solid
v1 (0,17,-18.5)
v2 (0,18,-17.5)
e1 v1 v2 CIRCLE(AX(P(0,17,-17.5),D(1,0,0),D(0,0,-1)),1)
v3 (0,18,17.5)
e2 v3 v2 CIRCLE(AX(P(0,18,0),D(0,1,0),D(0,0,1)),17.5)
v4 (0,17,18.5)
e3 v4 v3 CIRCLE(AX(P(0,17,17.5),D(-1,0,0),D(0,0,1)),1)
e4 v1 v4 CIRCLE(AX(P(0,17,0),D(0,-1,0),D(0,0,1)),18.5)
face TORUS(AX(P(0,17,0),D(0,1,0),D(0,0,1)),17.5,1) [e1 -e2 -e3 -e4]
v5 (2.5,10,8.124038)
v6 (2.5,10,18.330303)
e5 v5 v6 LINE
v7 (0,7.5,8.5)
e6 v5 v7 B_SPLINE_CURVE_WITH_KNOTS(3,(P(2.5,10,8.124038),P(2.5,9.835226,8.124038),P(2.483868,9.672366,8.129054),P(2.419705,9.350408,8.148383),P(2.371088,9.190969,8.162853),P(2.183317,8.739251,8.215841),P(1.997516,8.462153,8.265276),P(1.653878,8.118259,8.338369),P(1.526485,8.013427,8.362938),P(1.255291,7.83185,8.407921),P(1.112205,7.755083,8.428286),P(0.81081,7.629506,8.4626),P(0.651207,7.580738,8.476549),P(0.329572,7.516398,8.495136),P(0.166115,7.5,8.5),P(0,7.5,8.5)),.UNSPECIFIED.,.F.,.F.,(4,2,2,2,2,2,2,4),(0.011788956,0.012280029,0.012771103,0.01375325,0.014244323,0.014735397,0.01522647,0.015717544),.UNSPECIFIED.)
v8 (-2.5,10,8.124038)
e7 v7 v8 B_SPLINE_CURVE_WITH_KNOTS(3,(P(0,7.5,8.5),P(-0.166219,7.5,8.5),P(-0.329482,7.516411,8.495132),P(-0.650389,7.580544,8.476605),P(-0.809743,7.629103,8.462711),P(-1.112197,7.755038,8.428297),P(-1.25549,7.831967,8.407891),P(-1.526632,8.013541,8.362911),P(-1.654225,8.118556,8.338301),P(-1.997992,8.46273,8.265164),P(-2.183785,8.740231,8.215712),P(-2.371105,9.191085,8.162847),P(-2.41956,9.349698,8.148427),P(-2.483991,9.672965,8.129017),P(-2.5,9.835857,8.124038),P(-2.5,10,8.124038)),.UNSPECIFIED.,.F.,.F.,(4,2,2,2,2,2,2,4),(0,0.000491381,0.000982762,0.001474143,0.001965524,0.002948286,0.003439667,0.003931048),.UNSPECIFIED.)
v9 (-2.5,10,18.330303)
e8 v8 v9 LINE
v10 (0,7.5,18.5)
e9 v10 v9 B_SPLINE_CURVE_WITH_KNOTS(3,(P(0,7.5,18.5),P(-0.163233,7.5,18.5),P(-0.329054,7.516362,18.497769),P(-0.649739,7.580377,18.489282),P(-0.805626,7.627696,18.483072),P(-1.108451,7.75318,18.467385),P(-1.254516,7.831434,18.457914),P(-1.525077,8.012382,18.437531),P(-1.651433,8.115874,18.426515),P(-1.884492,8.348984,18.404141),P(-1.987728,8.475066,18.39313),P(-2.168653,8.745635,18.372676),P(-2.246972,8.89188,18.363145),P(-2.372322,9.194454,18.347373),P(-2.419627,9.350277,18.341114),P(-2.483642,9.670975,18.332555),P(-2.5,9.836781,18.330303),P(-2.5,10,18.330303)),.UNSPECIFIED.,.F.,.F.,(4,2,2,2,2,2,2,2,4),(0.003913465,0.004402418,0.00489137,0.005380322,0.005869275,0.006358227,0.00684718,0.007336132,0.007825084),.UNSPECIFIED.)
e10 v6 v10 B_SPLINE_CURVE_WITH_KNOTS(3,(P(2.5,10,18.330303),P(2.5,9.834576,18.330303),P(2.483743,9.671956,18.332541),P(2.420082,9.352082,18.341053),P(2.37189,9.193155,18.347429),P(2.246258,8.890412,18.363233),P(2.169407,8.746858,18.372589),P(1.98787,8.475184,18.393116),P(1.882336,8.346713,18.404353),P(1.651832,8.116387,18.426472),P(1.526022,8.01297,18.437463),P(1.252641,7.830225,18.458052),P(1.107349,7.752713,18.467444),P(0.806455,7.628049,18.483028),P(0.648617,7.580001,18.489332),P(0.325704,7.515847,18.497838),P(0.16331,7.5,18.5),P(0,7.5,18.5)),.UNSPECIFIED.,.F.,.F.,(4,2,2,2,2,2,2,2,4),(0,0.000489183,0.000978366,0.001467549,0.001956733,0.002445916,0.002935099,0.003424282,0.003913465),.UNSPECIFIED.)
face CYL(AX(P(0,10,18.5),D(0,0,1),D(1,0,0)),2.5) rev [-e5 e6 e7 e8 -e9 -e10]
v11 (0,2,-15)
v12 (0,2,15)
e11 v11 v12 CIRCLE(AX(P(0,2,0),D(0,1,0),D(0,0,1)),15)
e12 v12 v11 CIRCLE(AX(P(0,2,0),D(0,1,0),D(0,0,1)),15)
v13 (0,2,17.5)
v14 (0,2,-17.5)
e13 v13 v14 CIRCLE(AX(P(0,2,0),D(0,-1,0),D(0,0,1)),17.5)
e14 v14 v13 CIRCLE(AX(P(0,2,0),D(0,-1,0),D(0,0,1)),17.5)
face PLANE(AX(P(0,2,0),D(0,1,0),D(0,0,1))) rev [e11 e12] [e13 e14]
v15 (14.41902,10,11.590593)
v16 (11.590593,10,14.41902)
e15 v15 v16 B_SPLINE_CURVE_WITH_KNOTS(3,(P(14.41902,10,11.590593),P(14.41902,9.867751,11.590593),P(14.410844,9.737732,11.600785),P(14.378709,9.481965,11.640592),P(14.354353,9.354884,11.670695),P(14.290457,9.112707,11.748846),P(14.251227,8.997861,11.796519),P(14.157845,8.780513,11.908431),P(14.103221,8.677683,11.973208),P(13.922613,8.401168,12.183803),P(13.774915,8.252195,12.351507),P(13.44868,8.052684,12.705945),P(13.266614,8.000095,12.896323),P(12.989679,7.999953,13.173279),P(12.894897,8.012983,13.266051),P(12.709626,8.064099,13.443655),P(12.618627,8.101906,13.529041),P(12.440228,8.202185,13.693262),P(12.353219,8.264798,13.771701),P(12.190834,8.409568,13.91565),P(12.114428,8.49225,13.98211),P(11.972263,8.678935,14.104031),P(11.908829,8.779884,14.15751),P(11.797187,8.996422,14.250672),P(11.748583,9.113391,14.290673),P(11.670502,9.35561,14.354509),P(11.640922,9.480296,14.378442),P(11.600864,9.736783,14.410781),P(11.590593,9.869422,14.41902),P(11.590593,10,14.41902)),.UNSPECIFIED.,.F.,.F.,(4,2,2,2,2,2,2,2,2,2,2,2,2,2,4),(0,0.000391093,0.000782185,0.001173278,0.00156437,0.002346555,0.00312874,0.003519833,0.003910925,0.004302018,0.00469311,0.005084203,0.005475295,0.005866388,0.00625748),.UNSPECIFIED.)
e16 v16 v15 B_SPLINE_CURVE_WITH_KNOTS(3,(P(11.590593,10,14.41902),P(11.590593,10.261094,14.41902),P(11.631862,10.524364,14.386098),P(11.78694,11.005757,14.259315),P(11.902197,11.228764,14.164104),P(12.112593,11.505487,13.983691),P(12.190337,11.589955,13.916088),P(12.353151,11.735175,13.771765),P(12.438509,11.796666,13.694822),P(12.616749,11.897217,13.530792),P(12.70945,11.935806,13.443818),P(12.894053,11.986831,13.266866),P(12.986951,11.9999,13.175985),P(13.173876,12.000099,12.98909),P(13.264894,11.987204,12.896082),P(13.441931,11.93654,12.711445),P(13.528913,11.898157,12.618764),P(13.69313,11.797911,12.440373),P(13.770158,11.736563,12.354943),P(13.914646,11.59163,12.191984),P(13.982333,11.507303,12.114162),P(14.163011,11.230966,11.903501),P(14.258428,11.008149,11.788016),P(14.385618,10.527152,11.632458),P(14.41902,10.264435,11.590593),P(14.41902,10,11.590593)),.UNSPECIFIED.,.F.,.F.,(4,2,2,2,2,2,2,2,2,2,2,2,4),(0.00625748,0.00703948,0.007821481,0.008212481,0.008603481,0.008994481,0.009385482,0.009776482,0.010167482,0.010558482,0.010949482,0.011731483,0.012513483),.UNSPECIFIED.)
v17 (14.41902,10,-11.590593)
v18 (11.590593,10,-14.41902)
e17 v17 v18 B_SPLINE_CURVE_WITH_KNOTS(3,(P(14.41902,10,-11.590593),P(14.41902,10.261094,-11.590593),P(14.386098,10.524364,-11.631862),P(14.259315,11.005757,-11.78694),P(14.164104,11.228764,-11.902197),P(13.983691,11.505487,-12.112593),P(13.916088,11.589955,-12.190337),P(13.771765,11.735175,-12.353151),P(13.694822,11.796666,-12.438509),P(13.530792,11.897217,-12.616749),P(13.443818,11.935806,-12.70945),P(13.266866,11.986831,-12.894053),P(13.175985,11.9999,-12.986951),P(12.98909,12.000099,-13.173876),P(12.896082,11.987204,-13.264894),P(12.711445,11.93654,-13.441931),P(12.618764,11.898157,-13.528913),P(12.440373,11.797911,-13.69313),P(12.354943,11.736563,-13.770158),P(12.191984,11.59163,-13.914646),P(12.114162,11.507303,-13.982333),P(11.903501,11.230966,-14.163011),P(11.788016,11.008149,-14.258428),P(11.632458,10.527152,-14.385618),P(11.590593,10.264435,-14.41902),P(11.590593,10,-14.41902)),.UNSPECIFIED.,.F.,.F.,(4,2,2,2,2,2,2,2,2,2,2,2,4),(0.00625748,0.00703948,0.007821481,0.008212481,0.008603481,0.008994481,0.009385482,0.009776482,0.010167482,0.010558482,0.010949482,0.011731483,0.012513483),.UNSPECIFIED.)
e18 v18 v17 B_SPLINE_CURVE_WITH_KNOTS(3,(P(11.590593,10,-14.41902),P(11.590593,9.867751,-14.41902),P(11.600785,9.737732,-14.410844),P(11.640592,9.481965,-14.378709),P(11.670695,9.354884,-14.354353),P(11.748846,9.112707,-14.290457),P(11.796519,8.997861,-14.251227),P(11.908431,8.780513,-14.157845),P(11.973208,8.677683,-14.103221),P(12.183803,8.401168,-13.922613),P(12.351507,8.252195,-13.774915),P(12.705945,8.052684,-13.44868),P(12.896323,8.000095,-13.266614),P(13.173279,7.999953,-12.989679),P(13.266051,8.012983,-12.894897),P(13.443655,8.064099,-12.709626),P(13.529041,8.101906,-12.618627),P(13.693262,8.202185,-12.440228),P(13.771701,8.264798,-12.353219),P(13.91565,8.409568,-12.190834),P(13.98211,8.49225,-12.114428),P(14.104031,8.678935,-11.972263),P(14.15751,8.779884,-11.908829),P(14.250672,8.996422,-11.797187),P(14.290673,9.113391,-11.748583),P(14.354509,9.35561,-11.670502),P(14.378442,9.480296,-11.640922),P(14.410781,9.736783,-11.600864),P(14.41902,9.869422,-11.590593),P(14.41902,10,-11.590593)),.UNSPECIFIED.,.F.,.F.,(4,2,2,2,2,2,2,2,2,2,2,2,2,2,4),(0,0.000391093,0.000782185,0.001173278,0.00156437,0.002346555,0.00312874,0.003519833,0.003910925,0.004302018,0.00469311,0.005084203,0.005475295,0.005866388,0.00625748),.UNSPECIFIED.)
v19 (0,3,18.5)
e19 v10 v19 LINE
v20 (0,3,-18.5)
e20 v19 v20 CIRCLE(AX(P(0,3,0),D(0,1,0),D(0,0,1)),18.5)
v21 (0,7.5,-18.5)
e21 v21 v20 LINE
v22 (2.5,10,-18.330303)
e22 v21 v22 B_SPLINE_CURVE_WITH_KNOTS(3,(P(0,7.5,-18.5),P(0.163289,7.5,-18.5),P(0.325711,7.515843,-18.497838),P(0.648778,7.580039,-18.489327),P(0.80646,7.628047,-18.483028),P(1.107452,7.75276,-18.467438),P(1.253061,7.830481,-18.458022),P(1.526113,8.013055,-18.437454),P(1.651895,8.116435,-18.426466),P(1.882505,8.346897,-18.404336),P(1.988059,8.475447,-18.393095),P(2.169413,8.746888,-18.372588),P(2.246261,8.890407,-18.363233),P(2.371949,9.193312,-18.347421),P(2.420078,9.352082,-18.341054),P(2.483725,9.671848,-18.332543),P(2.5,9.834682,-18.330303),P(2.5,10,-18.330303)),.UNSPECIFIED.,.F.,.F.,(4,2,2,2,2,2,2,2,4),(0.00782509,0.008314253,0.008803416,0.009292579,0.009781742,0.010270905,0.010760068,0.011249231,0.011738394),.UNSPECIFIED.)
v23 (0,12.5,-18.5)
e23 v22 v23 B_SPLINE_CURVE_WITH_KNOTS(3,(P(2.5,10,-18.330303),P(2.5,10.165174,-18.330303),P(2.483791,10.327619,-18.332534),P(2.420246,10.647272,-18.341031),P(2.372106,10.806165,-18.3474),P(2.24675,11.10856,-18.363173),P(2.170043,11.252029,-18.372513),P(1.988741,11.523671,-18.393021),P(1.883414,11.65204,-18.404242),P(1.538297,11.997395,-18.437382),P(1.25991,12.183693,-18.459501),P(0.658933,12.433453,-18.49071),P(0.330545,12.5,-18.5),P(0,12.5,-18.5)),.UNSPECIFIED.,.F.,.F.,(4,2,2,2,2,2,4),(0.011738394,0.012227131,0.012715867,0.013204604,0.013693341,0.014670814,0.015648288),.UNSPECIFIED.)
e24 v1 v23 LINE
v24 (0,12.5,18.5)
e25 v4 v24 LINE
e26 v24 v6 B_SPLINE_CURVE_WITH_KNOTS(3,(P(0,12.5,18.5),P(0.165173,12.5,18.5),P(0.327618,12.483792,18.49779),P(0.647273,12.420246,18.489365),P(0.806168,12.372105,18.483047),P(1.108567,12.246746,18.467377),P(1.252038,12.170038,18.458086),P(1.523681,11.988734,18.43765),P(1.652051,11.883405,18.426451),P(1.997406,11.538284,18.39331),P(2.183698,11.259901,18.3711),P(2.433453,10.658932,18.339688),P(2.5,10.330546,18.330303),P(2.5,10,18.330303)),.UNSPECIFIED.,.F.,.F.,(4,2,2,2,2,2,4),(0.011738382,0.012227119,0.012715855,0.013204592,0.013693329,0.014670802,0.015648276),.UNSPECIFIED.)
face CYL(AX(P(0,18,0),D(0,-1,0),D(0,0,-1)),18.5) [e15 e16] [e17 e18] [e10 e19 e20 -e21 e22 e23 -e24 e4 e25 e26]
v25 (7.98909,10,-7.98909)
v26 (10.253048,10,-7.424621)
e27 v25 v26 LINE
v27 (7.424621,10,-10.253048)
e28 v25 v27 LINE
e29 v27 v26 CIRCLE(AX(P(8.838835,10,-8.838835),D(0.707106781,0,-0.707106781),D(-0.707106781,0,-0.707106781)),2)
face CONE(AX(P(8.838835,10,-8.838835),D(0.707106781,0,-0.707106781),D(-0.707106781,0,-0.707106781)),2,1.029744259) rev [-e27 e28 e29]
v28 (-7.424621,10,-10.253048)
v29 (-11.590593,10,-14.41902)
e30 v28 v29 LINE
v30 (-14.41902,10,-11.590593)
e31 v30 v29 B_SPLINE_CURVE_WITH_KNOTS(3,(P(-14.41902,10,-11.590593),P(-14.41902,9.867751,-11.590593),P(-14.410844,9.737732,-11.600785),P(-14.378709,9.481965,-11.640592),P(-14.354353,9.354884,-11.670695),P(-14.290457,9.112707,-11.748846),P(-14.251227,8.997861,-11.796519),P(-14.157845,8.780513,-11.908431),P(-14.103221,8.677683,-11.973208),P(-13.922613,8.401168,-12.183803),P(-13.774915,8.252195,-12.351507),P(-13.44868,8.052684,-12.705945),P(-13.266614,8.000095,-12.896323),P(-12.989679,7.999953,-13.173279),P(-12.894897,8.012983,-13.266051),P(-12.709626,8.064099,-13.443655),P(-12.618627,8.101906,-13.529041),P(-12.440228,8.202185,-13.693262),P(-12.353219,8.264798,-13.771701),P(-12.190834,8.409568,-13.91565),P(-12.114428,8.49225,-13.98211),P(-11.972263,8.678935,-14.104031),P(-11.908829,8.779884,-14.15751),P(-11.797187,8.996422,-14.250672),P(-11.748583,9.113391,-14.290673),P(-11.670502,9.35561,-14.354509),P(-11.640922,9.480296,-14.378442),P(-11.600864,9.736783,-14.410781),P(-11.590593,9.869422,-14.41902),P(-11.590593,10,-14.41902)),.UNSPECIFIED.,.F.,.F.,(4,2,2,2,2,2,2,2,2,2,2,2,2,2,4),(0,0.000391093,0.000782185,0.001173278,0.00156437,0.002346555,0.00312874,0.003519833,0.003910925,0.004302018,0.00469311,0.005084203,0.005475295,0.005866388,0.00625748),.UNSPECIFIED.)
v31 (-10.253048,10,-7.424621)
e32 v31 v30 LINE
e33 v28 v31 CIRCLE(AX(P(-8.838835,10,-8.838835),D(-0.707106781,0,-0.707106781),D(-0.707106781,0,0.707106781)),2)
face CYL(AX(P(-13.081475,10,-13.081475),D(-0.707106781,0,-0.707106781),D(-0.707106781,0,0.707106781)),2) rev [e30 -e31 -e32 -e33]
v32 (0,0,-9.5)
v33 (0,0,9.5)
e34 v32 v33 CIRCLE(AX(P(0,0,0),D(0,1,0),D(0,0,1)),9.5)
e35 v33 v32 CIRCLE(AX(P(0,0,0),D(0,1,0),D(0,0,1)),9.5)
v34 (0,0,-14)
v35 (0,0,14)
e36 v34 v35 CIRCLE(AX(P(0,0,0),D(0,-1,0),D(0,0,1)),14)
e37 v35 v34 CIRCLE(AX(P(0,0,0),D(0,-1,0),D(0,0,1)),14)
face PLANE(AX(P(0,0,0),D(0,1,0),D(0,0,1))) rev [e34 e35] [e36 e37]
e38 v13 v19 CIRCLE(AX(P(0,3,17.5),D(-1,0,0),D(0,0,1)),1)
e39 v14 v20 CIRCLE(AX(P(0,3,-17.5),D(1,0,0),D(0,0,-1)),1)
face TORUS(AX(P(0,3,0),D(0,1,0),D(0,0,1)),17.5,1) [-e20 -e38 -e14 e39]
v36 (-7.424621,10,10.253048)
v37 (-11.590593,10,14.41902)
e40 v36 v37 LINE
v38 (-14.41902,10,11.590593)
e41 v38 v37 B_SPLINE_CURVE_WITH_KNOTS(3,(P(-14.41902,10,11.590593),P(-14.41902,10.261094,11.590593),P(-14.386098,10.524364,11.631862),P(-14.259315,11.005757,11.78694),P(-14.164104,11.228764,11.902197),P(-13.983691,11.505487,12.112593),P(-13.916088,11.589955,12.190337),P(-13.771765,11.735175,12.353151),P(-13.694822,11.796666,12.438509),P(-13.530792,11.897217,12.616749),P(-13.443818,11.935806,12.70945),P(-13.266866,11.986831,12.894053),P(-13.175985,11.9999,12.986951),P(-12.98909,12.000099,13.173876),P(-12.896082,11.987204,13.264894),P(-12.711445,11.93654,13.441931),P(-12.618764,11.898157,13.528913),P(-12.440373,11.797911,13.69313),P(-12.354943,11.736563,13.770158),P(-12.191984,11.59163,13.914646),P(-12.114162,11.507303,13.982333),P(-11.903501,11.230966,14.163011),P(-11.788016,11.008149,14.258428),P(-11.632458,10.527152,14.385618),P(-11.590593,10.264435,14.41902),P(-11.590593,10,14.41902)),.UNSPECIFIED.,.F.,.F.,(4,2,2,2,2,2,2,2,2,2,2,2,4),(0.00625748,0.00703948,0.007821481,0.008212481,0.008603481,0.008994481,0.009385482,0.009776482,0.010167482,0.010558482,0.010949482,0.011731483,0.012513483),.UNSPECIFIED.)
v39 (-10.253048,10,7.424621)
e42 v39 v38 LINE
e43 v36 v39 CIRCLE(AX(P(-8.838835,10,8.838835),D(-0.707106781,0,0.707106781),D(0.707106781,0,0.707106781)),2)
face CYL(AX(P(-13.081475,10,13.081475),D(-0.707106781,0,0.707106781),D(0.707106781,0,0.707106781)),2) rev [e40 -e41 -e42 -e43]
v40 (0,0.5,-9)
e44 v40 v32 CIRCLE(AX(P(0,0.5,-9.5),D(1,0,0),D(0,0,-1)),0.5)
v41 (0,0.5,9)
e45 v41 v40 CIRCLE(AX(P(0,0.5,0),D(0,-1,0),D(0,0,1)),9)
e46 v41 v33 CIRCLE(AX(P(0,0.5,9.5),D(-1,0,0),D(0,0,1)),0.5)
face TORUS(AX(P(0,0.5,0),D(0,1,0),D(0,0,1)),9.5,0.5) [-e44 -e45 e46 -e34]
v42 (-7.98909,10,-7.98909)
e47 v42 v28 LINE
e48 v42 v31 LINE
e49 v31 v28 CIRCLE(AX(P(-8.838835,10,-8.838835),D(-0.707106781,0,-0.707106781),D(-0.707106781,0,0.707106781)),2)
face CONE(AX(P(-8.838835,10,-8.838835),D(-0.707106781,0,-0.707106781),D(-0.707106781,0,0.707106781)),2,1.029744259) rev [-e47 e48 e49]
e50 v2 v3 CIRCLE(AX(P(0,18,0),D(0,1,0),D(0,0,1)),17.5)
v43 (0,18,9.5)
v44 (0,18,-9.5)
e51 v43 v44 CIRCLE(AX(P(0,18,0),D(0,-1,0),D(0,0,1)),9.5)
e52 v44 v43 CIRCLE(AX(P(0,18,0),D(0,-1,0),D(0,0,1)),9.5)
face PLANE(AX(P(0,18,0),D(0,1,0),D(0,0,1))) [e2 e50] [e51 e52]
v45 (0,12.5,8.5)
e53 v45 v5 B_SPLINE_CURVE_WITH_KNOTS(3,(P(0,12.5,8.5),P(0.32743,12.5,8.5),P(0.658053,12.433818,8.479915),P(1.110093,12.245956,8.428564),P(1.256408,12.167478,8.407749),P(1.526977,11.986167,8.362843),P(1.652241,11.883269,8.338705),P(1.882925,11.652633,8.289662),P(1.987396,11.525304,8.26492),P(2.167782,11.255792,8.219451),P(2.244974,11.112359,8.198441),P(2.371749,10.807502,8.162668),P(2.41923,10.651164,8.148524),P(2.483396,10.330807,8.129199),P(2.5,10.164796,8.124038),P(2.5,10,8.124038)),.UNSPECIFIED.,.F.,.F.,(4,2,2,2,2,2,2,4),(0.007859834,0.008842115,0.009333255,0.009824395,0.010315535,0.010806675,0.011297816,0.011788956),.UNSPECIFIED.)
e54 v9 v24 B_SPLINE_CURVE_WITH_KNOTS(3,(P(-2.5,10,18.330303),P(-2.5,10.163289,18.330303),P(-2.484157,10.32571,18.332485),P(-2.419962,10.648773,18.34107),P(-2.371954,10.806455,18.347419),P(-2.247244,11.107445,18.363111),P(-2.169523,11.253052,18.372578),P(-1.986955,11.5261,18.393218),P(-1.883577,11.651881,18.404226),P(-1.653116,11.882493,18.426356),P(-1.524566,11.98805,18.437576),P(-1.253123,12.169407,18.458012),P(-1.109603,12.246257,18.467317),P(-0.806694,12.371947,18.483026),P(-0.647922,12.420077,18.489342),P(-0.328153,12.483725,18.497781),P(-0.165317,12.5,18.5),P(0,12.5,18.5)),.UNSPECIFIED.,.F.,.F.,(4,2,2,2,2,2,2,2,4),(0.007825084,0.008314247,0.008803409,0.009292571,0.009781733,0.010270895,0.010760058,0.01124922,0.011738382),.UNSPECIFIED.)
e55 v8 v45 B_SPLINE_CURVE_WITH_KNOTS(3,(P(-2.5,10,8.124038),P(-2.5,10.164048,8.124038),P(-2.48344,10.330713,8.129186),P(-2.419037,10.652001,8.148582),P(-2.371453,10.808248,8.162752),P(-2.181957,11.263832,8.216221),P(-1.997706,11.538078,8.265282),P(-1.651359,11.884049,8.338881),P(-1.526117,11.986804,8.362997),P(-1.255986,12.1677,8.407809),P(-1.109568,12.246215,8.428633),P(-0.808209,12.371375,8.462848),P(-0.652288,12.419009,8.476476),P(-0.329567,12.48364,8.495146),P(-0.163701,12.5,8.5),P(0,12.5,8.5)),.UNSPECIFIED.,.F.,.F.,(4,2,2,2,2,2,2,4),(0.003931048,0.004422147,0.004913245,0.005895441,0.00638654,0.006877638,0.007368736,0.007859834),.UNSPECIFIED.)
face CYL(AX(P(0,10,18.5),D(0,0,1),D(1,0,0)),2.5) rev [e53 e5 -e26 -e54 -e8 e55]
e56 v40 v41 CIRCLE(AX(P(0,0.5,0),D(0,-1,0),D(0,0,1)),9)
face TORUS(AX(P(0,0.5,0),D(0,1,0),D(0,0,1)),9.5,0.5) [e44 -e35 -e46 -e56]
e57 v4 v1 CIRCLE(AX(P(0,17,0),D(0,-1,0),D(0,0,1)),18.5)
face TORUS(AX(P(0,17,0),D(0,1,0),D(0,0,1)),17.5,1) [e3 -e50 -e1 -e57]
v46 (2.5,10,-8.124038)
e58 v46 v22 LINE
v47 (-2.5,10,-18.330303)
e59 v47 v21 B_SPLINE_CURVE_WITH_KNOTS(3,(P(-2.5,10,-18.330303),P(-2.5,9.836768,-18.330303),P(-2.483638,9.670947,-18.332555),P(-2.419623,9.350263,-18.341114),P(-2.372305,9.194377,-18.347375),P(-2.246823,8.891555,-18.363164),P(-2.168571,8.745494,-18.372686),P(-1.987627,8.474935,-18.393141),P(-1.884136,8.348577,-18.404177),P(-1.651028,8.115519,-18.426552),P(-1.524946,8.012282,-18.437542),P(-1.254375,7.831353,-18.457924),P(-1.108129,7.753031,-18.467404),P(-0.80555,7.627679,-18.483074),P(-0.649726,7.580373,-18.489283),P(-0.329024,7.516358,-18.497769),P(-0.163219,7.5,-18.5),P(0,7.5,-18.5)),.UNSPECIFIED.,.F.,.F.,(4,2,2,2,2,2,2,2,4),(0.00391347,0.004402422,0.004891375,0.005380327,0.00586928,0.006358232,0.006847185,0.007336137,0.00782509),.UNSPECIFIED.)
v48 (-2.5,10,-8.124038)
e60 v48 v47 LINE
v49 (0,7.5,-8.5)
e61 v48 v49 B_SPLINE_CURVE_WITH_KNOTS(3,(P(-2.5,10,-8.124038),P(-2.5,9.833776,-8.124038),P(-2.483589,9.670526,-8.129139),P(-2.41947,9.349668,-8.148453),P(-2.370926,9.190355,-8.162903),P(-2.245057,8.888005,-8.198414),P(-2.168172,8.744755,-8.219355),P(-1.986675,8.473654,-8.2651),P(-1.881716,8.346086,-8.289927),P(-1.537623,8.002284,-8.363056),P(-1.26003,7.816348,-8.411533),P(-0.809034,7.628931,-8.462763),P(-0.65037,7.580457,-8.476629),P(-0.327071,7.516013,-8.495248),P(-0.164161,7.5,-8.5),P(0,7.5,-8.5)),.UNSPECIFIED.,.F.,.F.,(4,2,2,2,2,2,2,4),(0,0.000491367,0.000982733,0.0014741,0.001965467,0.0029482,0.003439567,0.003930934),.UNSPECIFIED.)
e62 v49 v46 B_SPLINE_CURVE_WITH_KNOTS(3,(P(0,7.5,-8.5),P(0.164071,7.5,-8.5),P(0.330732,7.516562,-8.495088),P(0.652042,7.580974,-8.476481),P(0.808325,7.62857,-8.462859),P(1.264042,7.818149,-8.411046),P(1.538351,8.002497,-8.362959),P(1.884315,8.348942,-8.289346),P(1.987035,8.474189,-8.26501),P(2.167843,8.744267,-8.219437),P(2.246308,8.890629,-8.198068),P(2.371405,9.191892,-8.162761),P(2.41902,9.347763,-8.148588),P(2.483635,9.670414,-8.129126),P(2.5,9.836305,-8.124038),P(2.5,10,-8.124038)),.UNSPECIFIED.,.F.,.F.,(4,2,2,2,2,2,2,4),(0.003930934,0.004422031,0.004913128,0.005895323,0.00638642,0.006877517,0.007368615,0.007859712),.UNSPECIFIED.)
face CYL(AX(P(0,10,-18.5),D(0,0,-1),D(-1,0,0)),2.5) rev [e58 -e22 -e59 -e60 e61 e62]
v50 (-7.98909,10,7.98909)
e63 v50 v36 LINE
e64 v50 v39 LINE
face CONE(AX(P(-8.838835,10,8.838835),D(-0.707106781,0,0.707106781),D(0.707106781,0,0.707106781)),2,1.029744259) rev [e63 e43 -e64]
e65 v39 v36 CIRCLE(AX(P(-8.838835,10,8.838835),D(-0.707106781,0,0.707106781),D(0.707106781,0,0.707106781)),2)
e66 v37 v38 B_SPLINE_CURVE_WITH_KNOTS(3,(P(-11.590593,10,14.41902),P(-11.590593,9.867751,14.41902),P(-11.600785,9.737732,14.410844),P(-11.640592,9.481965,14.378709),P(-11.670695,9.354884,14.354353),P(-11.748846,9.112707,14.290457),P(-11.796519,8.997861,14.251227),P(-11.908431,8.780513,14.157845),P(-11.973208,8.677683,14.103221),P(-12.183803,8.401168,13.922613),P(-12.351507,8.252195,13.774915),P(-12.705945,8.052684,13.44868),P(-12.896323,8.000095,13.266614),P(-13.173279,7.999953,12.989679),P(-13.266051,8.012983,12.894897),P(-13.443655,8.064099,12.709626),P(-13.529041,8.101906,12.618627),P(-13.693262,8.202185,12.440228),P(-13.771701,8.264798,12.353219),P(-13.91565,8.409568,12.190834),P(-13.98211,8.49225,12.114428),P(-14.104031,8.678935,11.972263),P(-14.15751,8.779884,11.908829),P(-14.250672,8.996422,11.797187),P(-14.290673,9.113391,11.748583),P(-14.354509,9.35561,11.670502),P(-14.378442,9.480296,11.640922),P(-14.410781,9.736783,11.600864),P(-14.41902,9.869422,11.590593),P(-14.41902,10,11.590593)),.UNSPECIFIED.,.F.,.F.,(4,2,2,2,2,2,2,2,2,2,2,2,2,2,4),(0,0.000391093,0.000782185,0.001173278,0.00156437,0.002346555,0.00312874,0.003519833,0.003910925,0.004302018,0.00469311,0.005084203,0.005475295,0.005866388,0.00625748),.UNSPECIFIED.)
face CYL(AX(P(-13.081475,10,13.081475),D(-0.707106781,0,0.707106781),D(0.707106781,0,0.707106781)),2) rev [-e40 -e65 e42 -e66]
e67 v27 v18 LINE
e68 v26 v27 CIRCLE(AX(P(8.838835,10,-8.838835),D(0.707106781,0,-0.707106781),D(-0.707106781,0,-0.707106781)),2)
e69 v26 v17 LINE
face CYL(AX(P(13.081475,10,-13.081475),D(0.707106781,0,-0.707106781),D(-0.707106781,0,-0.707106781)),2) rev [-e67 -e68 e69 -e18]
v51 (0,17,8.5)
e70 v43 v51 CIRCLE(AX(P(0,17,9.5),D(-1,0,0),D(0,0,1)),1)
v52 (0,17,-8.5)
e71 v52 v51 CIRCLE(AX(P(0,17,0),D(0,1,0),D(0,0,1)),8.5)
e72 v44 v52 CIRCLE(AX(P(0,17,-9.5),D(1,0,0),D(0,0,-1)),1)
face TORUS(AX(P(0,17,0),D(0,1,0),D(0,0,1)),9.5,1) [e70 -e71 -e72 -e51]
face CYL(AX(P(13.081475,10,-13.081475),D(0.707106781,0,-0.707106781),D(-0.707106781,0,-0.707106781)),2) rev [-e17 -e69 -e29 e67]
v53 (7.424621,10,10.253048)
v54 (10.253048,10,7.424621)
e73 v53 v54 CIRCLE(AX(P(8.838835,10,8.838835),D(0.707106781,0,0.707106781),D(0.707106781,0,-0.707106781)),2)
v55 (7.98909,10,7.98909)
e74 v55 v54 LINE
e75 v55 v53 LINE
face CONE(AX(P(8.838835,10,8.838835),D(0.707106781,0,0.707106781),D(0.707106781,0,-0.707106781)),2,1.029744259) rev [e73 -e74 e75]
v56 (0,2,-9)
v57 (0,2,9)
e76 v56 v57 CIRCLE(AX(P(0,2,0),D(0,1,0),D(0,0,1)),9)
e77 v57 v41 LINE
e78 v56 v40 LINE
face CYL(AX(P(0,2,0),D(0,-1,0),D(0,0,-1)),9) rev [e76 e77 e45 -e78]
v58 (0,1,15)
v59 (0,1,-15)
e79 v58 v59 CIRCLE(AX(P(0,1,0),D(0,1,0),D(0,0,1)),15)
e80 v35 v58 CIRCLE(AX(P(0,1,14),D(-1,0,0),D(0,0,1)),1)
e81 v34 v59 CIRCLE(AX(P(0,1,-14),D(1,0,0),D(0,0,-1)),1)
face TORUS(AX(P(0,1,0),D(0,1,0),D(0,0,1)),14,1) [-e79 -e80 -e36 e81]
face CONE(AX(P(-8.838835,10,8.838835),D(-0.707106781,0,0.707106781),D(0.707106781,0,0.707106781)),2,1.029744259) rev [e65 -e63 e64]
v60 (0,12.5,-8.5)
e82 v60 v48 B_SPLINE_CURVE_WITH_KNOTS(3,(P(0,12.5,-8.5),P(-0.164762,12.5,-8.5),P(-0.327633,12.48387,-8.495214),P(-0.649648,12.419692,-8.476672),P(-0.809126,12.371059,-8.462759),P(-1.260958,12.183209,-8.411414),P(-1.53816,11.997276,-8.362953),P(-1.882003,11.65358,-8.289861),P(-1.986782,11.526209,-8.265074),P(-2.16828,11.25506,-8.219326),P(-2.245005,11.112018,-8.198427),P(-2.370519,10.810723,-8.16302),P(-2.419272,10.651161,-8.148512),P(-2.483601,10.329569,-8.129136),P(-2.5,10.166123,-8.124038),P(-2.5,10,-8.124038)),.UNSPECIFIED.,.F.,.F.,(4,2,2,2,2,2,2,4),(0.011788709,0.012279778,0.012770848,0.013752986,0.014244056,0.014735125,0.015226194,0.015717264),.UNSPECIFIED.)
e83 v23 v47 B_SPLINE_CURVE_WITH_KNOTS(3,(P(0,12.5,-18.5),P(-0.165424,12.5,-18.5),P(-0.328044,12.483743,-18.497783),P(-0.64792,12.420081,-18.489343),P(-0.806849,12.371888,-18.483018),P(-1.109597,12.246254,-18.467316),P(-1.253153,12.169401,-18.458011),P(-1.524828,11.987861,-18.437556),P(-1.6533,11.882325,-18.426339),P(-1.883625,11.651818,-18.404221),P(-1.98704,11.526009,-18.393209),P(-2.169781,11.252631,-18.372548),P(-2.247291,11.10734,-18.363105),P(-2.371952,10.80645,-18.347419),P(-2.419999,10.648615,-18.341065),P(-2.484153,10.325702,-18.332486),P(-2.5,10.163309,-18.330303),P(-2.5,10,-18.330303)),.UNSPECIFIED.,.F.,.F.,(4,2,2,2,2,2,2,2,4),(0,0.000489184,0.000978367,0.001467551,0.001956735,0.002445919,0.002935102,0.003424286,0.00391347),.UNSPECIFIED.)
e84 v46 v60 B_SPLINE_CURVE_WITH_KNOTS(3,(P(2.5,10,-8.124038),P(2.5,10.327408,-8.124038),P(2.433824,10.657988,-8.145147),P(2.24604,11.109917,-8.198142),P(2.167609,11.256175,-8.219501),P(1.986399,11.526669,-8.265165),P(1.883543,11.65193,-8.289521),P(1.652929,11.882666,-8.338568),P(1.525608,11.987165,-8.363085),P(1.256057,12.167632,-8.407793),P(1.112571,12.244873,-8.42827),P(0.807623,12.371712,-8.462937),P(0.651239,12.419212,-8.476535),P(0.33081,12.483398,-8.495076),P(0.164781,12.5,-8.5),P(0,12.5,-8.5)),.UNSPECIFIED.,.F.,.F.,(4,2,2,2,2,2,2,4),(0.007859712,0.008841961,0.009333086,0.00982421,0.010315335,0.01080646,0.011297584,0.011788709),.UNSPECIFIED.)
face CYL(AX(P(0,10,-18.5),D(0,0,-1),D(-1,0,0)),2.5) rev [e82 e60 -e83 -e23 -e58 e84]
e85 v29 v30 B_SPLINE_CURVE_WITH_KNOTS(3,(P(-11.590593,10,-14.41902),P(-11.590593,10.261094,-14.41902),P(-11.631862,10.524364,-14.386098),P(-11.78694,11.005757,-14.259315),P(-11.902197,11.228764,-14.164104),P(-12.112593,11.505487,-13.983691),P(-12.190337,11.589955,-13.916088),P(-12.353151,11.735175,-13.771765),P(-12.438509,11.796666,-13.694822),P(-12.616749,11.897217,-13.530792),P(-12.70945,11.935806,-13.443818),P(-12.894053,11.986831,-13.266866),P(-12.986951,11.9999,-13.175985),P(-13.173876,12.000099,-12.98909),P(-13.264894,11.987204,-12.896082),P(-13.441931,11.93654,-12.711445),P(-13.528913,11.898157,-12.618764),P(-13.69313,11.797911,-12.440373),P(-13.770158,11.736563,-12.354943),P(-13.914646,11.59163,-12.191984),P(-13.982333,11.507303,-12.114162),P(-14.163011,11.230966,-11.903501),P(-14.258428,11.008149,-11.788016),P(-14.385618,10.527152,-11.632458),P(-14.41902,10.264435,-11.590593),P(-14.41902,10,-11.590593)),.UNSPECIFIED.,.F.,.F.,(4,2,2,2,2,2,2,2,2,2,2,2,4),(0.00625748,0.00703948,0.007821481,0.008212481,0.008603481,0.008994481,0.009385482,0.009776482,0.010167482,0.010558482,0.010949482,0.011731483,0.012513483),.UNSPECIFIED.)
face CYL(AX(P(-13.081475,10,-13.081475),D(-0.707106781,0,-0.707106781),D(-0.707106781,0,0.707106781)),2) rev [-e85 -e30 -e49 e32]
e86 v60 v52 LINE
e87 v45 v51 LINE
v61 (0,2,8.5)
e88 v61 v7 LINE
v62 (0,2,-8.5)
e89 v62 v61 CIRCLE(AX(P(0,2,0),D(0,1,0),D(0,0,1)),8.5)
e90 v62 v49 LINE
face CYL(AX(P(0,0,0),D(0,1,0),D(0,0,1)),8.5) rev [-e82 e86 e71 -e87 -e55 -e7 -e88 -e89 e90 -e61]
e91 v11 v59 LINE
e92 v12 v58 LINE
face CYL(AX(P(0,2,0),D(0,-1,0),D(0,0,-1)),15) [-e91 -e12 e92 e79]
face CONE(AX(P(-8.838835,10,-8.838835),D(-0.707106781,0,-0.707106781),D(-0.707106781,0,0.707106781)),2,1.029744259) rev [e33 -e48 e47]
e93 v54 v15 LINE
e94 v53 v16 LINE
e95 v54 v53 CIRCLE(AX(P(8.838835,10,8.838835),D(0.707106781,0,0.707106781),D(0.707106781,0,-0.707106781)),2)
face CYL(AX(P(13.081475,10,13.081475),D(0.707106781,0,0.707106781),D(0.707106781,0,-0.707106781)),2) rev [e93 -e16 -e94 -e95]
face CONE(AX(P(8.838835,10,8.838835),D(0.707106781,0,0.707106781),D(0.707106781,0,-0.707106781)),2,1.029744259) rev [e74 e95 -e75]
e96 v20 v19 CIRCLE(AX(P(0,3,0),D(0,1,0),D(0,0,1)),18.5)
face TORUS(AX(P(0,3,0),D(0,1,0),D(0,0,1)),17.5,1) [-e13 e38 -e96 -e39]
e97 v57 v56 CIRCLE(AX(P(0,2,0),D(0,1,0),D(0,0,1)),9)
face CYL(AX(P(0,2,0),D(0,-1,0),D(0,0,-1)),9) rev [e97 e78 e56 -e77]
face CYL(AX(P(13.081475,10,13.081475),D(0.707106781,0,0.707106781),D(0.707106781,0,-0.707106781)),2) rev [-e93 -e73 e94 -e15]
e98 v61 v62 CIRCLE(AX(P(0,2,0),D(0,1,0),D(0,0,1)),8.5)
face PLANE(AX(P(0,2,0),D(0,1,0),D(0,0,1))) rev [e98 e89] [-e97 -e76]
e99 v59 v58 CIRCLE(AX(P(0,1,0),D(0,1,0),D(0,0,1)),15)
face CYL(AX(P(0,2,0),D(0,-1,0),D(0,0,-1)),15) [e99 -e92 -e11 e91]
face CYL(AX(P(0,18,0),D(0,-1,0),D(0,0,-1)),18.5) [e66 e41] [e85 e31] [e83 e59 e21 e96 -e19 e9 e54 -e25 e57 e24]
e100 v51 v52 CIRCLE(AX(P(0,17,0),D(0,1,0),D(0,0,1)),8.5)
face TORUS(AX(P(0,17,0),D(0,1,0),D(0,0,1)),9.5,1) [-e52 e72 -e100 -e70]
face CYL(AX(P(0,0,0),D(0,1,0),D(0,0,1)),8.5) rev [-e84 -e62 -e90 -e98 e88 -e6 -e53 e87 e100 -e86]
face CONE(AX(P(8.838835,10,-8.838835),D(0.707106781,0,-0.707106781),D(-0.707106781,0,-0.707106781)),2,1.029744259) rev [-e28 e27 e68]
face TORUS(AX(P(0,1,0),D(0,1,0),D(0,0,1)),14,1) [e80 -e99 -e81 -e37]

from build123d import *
from build123d.topology import SkipClean

# Parameters (mm, degrees)
SKETCH_1_R               = 15
SKETCH_1_R_2             = 9
EXTRUDE_1_DEPTH          = 2
SKETCH_2_R               = 18.5
EXTRUDE_2_DEPTH          = 16
SKETCH_3_R               = 8.5
CUT_EXTRUDE_1_DEPTH      = 32.756889016
FILLET_1_R               = 1
FILLET_2_R               = 1
FILLET_3_R               = 0.5
HOLE_WIZARD_M6_1_D       = 5
HOLE_WIZARD_M6_1_DEPTH   = 8.5
HOLE_WIZARD_M6_1_TIP     = 1.502151548
PATTERN_CIRCULAR_1_COUNT = 4
HOLE_WIZARD_M6_2_D       = 5
HOLE_WIZARD_M6_2_DEPTH   = 8.5
HOLE_WIZARD_M6_2_TIP     = 1.502151548
CUT_EXTRUDE_2_DEPTH      = 21
CUT_EXTRUDE_2_DEPTH_BACK = 24
SKETCH_15_R              = 2.5


with BuildPart() as part:
    # 草图1 → 拉伸1 (new body)
    with BuildSketch(Plane(origin=(0, 0, 0), x_dir=(1, 0, 0), z_dir=(0, 1, 0))):
        with Locations(Location((0, 0, 0), (0, 0, 270))):
            Circle(SKETCH_1_R)
        with Locations(Location((0, 0, 0), (0, 0, 270))):
            Circle(SKETCH_1_R_2, mode=Mode.SUBTRACT)
    extrude(amount=EXTRUDE_1_DEPTH)

    # 草图2 → 拉伸2 (add)
    with BuildSketch(Plane(origin=(0, 2, 0), x_dir=(-1, 0, 0), z_dir=(0, 1, 0))):
        with Locations(Location((0, 0, 0), (0, 0, 90))):
            Circle(SKETCH_2_R)
    extrude(amount=EXTRUDE_2_DEPTH)

    # 草图3 → 切除-拉伸1 (cut, through all)
    with BuildSketch(Plane(origin=(0, 18, 0), x_dir=(-1, 0, 0), z_dir=(0, 1, 0))):
        with Locations(Location((0, 0, 0), (0, 0, 90))):
            Circle(SKETCH_3_R)
    extrude(amount=-CUT_EXTRUDE_1_DEPTH, mode=Mode.SUBTRACT)

    # 圆角1
    fillet_1_edges = [part.edges().sort_by_distance(p)[0] for p in [
        (0, 2, -18.5),
        (0, 18, -18.5),
    ]]
    fillet(fillet_1_edges, radius=FILLET_1_R)

    # 圆角2
    fillet_2_edges = [part.edges().sort_by_distance(p)[0] for p in [
        (0, 18, -8.5),
        (0, 0, -15),
    ]]
    fillet(fillet_2_edges, radius=FILLET_2_R)

    # 圆角3
    fillet_3_edges = [part.edges().sort_by_distance(p)[0] for p in [
        (0, 0, -9),
    ]]
    fillet(fillet_3_edges, radius=FILLET_3_R)

    # M6 螺纹孔1
    with Locations(Plane.XY.offset(18.5)):
        with Locations((0, 10)):
            Hole(HOLE_WIZARD_M6_1_D / 2, depth=HOLE_WIZARD_M6_1_DEPTH)
            with Locations((0, 0, -(HOLE_WIZARD_M6_1_DEPTH + HOLE_WIZARD_M6_1_TIP / 2))):  # 118° drill point
                Cone(0, HOLE_WIZARD_M6_1_D / 2, HOLE_WIZARD_M6_1_TIP, mode=Mode.SUBTRACT)

    # 草图11 → Ø4.0 (4) 直径孔1 (revolve, cut)
    with BuildSketch(Plane(origin=(13.081475452, 10, -13.081475452), x_dir=(-0.7071067811865462, 0, -0.7071067811865488), z_dir=(0, 1, 0))):
        Polygon((0, 0), (0, 7.201721238), (2, 6), (2, 0), align=None)
    hole_wizard_4_0_4_1 = revolve(axis=Axis((17.571603512, 10, -17.571603512), (-0.7071067811865488, 0, 0.7071067811865464)), mode=Mode.SUBTRACT)

    # 阵列(圆周)1: Ø4.0 (4) 直径孔1 ×4 about axis
    pattern_circular_1_axis = Axis((0, 0, 0), (0, 1, 0))
    for i in range(1, PATTERN_CIRCULAR_1_COUNT):
        add(hole_wizard_4_0_4_1.rotate(pattern_circular_1_axis, i * 360 / PATTERN_CIRCULAR_1_COUNT), mode=Mode.SUBTRACT)

    # M6 螺纹孔2
    with Locations(Plane(origin=(0, 10, -18.5), x_dir=(-1, 0, 0), z_dir=(0, 0, -1))):
        with Locations((0, 0)):
            Hole(HOLE_WIZARD_M6_2_D / 2, depth=HOLE_WIZARD_M6_2_DEPTH)
            with Locations((0, 0, -(HOLE_WIZARD_M6_2_DEPTH + HOLE_WIZARD_M6_2_TIP / 2))):  # 118° drill point
                Cone(0, HOLE_WIZARD_M6_2_D / 2, HOLE_WIZARD_M6_2_TIP, mode=Mode.SUBTRACT)

    # 草图15 → 切除-拉伸2 (cut, two sides: drawn at the far end of the back side and taken through both)
    with SkipClean():  # the faces are left unmerged after this step: merging them gives an invalid solid
        with BuildSketch(Plane.XY.offset(-CUT_EXTRUDE_2_DEPTH_BACK)):
            with Locations(Location((0, 10, 0), (0, 0, 269.999999977))):
                Circle(SKETCH_15_R)
        extrude(amount=CUT_EXTRUDE_2_DEPTH + CUT_EXTRUDE_2_DEPTH_BACK, mode=Mode.SUBTRACT)


solid = part.part
